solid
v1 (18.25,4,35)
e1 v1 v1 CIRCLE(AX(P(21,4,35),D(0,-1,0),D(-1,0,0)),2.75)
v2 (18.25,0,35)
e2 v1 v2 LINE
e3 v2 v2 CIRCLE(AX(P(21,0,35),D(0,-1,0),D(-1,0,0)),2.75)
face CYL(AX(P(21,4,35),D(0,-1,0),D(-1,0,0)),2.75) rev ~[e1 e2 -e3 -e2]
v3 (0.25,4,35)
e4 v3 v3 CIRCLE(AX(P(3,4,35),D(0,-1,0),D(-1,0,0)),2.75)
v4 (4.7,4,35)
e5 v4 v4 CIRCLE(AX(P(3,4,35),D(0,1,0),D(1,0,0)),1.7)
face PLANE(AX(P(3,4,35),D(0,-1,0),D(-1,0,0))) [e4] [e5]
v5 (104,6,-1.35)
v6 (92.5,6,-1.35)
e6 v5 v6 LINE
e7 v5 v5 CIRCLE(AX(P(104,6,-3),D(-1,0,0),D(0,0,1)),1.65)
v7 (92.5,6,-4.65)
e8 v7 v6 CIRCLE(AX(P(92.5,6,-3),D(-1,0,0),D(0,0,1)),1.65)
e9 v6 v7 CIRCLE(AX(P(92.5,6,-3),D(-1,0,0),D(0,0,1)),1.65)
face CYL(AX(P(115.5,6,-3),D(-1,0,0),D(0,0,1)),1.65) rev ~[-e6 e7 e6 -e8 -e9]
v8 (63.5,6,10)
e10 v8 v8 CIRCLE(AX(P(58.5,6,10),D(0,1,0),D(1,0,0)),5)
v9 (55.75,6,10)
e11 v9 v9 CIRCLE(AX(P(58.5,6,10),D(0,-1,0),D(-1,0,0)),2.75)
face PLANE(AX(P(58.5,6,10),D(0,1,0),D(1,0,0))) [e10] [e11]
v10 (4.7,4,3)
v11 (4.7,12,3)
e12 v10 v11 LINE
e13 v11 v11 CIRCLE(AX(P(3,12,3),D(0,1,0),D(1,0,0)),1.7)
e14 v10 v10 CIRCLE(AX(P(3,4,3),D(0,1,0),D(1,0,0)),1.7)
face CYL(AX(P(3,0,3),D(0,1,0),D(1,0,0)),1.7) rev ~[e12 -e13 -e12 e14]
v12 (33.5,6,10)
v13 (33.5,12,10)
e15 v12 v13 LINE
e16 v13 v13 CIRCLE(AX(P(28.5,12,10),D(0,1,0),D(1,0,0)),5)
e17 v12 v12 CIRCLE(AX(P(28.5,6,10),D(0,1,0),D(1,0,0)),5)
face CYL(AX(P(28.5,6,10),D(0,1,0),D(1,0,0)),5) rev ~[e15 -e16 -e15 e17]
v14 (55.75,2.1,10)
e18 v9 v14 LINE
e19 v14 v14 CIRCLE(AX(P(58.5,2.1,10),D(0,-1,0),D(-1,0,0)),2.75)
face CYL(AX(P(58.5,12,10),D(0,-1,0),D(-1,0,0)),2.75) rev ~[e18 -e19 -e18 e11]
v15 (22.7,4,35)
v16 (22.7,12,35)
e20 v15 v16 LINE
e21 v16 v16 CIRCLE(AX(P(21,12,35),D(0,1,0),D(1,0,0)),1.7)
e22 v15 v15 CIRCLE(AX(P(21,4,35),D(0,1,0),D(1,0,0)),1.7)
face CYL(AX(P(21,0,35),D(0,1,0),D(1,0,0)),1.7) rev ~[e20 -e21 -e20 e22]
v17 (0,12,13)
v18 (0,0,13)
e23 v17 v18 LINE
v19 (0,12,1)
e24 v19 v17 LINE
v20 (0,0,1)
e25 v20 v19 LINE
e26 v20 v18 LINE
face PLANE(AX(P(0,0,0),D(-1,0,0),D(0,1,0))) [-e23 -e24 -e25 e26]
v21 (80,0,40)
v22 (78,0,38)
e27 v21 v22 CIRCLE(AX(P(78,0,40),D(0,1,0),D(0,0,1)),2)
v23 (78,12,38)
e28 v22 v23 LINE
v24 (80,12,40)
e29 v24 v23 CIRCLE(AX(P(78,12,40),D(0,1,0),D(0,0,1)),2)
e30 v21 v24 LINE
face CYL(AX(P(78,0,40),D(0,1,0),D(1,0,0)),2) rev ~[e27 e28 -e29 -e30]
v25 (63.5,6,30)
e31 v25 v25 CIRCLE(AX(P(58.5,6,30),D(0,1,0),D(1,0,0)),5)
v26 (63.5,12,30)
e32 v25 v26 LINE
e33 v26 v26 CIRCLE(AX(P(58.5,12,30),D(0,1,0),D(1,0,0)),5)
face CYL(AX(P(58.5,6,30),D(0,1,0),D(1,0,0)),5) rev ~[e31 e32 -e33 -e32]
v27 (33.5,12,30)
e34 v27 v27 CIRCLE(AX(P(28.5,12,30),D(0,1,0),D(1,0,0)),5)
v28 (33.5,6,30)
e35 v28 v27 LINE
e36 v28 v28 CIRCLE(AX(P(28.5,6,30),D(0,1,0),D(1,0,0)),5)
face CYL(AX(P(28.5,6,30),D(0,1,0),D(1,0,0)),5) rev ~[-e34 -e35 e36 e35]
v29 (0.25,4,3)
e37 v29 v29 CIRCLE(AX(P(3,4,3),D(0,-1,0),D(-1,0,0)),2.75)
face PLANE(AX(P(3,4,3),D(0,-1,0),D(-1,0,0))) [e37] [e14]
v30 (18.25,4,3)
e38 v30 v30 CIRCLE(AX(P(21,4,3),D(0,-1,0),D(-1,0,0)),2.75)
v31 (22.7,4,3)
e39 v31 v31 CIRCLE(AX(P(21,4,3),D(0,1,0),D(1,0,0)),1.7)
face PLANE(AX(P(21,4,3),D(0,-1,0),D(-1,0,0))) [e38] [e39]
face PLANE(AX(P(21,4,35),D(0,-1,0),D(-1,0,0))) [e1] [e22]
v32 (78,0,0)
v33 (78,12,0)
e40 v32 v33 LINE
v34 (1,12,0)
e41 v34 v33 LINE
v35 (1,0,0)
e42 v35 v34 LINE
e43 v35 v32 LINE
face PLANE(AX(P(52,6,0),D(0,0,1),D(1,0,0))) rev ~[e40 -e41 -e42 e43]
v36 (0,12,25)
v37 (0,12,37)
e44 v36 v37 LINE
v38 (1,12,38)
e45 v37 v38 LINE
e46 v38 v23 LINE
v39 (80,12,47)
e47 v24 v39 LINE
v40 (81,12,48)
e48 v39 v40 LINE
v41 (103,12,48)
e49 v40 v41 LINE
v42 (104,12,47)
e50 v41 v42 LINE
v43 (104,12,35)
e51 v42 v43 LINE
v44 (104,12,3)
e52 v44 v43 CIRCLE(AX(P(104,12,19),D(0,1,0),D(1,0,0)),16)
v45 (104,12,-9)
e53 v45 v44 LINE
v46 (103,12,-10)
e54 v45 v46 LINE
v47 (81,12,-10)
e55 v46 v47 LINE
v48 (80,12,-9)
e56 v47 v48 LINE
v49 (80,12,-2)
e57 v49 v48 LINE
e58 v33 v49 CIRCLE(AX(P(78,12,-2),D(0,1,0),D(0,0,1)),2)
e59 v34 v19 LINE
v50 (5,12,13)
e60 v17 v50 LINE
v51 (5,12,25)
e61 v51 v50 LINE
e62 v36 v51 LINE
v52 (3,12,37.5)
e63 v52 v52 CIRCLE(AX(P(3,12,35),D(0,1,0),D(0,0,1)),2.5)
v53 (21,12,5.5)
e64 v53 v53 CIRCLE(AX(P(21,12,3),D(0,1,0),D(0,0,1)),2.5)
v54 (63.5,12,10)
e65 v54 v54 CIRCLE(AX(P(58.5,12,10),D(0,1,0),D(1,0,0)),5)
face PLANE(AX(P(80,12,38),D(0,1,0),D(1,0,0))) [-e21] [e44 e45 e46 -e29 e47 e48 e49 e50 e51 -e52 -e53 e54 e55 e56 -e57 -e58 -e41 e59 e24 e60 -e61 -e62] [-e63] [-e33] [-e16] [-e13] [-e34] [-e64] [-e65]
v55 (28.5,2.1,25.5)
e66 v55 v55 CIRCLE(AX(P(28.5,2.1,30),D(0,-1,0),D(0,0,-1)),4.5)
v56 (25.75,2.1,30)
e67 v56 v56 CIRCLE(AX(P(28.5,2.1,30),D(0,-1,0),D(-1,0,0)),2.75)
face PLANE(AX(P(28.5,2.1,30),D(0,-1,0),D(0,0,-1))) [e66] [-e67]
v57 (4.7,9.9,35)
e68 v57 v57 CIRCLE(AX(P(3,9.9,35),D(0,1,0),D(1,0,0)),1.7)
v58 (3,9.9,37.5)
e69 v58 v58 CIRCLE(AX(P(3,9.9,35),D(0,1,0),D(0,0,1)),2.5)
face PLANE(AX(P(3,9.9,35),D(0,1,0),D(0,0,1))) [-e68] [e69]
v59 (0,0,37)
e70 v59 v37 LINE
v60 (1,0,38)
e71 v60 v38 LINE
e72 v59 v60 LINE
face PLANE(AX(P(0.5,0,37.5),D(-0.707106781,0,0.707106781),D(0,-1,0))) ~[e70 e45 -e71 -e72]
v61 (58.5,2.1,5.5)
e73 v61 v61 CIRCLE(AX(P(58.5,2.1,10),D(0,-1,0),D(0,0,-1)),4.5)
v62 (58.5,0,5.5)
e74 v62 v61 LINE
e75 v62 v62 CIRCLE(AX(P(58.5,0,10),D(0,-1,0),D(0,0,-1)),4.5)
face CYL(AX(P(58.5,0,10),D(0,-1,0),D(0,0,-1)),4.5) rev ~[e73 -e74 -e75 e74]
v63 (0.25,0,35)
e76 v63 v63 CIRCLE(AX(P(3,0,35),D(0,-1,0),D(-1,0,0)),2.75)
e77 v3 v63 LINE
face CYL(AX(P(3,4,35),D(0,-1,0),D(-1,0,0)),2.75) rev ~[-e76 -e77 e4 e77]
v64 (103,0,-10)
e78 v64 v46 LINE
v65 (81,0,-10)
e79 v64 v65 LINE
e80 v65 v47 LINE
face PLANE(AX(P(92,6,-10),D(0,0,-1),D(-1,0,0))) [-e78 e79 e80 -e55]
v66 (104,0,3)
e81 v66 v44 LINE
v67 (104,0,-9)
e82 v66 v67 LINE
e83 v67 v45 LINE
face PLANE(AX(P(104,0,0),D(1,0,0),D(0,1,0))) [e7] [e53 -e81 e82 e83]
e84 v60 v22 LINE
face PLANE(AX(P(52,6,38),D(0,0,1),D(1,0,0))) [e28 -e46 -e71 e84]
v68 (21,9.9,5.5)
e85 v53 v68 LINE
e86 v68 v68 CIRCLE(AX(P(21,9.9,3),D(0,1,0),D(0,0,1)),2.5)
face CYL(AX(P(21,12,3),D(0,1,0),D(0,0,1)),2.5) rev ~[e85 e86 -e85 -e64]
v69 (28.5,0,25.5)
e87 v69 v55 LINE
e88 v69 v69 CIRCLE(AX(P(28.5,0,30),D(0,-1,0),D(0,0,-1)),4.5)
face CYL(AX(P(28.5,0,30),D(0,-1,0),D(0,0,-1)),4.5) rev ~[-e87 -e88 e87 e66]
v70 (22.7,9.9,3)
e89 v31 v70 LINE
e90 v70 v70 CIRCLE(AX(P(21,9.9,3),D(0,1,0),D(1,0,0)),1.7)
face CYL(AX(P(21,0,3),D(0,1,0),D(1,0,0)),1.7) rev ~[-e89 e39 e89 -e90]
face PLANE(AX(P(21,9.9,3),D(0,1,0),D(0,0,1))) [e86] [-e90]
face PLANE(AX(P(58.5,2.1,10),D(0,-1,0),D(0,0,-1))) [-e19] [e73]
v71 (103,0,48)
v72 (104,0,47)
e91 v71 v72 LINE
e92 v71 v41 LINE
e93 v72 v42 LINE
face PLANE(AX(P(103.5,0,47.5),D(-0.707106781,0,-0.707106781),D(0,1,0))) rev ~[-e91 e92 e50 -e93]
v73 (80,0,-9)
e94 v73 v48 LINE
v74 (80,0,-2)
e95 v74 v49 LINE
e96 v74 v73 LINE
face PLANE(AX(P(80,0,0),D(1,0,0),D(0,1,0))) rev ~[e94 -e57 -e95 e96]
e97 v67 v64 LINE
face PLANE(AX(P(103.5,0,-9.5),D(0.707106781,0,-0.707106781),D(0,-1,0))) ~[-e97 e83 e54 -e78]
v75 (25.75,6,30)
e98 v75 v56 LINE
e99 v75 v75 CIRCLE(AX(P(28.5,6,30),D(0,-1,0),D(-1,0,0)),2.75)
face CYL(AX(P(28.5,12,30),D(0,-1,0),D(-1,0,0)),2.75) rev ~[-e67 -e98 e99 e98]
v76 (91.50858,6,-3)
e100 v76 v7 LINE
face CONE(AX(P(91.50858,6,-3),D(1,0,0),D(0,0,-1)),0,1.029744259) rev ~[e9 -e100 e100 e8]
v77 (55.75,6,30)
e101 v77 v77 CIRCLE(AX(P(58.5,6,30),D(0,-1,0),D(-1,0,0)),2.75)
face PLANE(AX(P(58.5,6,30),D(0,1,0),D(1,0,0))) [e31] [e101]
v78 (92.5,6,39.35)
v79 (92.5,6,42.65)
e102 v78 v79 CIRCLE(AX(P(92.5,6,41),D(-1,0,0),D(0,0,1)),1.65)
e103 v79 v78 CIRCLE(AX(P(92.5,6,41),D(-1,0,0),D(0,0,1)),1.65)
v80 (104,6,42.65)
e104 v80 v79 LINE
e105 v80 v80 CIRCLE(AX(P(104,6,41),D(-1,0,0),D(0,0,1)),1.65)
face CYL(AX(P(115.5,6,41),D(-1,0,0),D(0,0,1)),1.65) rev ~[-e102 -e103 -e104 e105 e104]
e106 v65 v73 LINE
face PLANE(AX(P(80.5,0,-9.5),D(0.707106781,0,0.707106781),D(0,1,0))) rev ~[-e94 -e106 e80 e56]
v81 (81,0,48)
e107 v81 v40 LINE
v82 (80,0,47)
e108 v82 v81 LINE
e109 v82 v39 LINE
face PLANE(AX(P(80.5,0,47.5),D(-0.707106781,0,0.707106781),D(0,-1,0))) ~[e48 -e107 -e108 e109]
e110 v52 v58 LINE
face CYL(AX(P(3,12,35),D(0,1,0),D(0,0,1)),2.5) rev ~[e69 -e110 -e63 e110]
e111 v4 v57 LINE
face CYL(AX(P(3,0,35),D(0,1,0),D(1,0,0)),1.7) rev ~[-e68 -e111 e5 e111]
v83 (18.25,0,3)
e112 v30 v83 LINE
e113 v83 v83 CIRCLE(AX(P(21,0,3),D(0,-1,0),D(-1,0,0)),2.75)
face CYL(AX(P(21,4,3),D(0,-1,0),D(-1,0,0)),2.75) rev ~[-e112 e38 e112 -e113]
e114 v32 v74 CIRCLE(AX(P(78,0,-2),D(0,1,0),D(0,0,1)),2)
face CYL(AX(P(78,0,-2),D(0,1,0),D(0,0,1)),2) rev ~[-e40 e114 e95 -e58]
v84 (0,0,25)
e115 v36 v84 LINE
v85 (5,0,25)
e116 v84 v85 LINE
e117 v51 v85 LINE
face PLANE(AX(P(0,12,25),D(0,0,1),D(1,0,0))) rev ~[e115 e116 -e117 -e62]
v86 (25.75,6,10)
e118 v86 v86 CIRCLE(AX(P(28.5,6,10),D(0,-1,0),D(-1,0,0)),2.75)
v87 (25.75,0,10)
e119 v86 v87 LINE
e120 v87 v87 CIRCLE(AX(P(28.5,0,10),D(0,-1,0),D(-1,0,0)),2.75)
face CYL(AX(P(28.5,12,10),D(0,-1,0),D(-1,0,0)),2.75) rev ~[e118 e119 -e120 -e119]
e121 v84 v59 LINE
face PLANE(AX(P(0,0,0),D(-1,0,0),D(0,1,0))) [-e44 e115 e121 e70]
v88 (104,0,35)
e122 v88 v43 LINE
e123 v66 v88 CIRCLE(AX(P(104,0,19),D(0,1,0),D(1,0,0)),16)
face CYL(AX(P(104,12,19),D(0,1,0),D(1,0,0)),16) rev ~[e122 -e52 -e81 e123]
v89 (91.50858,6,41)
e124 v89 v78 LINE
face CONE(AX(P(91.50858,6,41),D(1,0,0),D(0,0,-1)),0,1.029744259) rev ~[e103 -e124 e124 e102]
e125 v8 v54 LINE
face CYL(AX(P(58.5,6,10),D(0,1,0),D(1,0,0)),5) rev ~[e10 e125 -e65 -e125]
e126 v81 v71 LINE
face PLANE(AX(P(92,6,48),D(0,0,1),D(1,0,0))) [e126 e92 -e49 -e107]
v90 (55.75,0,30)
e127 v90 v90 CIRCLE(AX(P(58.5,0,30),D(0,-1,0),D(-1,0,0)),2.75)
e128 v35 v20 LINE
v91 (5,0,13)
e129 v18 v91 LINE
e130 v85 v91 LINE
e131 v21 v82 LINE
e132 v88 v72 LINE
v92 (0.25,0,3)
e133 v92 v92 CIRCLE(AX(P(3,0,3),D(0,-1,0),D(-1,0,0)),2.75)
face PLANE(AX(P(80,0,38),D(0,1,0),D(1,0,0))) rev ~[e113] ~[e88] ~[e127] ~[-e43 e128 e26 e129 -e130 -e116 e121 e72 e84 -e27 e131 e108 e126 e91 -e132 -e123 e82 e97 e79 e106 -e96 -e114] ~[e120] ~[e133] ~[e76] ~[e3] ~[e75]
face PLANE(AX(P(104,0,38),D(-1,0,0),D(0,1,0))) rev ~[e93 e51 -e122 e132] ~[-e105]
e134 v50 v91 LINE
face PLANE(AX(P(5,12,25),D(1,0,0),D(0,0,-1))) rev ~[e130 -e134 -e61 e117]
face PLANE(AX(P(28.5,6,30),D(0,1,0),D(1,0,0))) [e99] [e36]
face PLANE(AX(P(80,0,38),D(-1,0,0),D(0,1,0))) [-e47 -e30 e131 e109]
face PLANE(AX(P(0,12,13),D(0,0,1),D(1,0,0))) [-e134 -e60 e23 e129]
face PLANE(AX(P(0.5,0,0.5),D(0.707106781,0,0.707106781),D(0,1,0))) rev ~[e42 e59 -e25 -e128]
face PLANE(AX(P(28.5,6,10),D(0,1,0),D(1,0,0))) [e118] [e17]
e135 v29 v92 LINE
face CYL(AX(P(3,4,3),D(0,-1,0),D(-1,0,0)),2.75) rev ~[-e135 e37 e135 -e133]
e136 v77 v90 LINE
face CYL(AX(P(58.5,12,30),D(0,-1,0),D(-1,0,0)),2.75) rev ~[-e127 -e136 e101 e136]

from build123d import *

# Parameters (mm, degrees)
SKETCH1_W                                            = 104
SKETCH1_H                                            = 12
BOSS_EXTRUDE1_DEPTH                                  = 38
SKETCH2_W                                            = 5
SKETCH2_H                                            = 12
CUT_EXTRUDE1_DEPTH                                   = 112.373246339
SKETCH3_R                                            = 16
CUT_EXTRUDE2_DEPTH                                   = 112.373246339
SKETCH4_W                                            = 24
SKETCH4_H                                            = 12
BOSS_EXTRUDE2_DEPTH                                  = 10
SKETCH5_W                                            = 24
SKETCH5_H                                            = 12
BOSS_EXTRUDE3_DEPTH                                  = 10
CHAMFER1_SIZE                                        = 1
FILLET1_R                                            = 2
HOLE_SIZE_PER_SOCKET_HEAD_CAP_SCREW_TYPE_D           = 3.4
HOLE_SIZE_PER_SOCKET_HEAD_CAP_SCREW_TYPE_CBORE_D     = 5.5
HOLE_SIZE_PER_SOCKET_HEAD_CAP_SCREW_TYPE_CBORE_DEPTH = 4
SKETCH8_R                                            = 2.5
CUT_EXTRUDE3_DEPTH                                   = 2.1
HOLE_SIZE_PER_SOCKET_HEAD_CAP_SCREW_2_D              = 5.5
HOLE_SIZE_PER_SOCKET_HEAD_CAP_SCREW_2_CBORE_D        = 10
HOLE_SIZE_PER_SOCKET_HEAD_CAP_SCREW_2_CBORE_DEPTH    = 6
SKETCH11_R                                           = 4.5
CUT_EXTRUDE4_DEPTH                                   = 2.1
M4_TAPPED_HOLE1_D                                    = 3.3
M4_TAPPED_HOLE1_DEPTH                                = 11.5
M4_TAPPED_HOLE1_TIP                                  = 0.991420021


with BuildPart() as part:
    # Sketch1 → Boss-Extrude1 (new body)
    with BuildSketch(Plane.XY):
        with Locations((52, 6)):
            Rectangle(SKETCH1_W, SKETCH1_H)
    extrude(amount=BOSS_EXTRUDE1_DEPTH)

    # Sketch2 → Cut-Extrude1 (cut, through all)
    with BuildSketch(Plane(origin=(0, 12, 0), x_dir=(1, 0, 0), z_dir=(0, 1, 0))):
        with Locations((2.5, -19)):
            Rectangle(SKETCH2_W, SKETCH2_H)
    extrude(amount=-CUT_EXTRUDE1_DEPTH, mode=Mode.SUBTRACT)

    # Sketch3 → Cut-Extrude2 (cut, through all)
    with BuildSketch(Plane(origin=(0, 12, 0), x_dir=(1, 0, 0), z_dir=(0, 1, 0))):
        with Locations((104, -19)):
            Circle(SKETCH3_R)
    extrude(amount=-CUT_EXTRUDE2_DEPTH, mode=Mode.SUBTRACT)

    # Sketch4 → Boss-Extrude2 (add)
    with BuildSketch(Plane(origin=(0, 0, 0), x_dir=(-1, 0, 0), z_dir=(0, 0, -1))):
        with Locations((-92, 6)):
            Rectangle(SKETCH4_W, SKETCH4_H)
    extrude(amount=BOSS_EXTRUDE2_DEPTH)

    # Sketch5 → Boss-Extrude3 (add)
    with BuildSketch(Plane.XY.offset(38)):
        with Locations((92, 6)):
            Rectangle(SKETCH5_W, SKETCH5_H)
    extrude(amount=BOSS_EXTRUDE3_DEPTH)

    # Chamfer1
    chamfer1_edges = [part.edges().sort_by_distance(p)[0] for p in [
        (0, 6, 0),
        (0, 6, 38),
        (104, 6, 48),
        (80, 6, 48),
        (104, 6, -10),
        (80, 6, -10),
    ]]
    chamfer(chamfer1_edges, length=CHAMFER1_SIZE)

    # Fillet1
    fillet1_edges = [part.edges().sort_by_distance(p)[0] for p in [
        (80, 6, 38),
        (80, 6, 0),
    ]]
    fillet(fillet1_edges, radius=FILLET1_R)

    # Hole size per socket head cap screw type (through all)
    with Locations(Plane(origin=(0, 0, 0), x_dir=(-1, 0, 0), z_dir=(0, -1, 0))):
        with Locations((-3, -35), (-21, -3), (-3, -3), (-21, -35)):
            CounterBoreHole(HOLE_SIZE_PER_SOCKET_HEAD_CAP_SCREW_TYPE_D / 2, HOLE_SIZE_PER_SOCKET_HEAD_CAP_SCREW_TYPE_CBORE_D / 2, HOLE_SIZE_PER_SOCKET_HEAD_CAP_SCREW_TYPE_CBORE_DEPTH)

    # Sketch8 → Cut-Extrude3 (cut)
    with BuildSketch(Plane(origin=(0, 12, 0), x_dir=(1, 0, 0), z_dir=(0, 1, 0))):
        with Locations(Location((3, -35, 0), (0, 0, 270))):
            Circle(SKETCH8_R)
        with Locations(Location((21, -3, 0), (0, 0, 270))):
            Circle(SKETCH8_R)
    extrude(amount=-CUT_EXTRUDE3_DEPTH, mode=Mode.SUBTRACT)

    # Hole size per socket head cap screw  2 (through all)
    with Locations(Plane(origin=(0, 12, 0), x_dir=(1, 0, 0), z_dir=(0, 1, 0))):
        with Locations((28.5, -10), (28.5, -30), (58.5, -10), (58.5, -30)):
            CounterBoreHole(HOLE_SIZE_PER_SOCKET_HEAD_CAP_SCREW_2_D / 2, HOLE_SIZE_PER_SOCKET_HEAD_CAP_SCREW_2_CBORE_D / 2, HOLE_SIZE_PER_SOCKET_HEAD_CAP_SCREW_2_CBORE_DEPTH)

    # Sketch11 → Cut-Extrude4 (cut)
    with BuildSketch(Plane.XZ):
        with Locations(Location((28.5, 30, 0), (0, 0, 270))):
            Circle(SKETCH11_R)
        with Locations(Location((58.5, 10, 0), (0, 0, 270))):
            Circle(SKETCH11_R)
    extrude(amount=-CUT_EXTRUDE4_DEPTH, mode=Mode.SUBTRACT)

    # M4 Tapped Hole1
    with Locations(Plane(origin=(104, 0, 0), x_dir=(0, 0, -1), z_dir=(1, 0, 0))):
        with Locations((3, 6), (-41, 6)):
            Hole(M4_TAPPED_HOLE1_D / 2, depth=M4_TAPPED_HOLE1_DEPTH)
            with Locations((0, 0, -(M4_TAPPED_HOLE1_DEPTH + M4_TAPPED_HOLE1_TIP / 2))):  # 118° drill point
                Cone(0, M4_TAPPED_HOLE1_D / 2, M4_TAPPED_HOLE1_TIP, mode=Mode.SUBTRACT)


solid = part.part
